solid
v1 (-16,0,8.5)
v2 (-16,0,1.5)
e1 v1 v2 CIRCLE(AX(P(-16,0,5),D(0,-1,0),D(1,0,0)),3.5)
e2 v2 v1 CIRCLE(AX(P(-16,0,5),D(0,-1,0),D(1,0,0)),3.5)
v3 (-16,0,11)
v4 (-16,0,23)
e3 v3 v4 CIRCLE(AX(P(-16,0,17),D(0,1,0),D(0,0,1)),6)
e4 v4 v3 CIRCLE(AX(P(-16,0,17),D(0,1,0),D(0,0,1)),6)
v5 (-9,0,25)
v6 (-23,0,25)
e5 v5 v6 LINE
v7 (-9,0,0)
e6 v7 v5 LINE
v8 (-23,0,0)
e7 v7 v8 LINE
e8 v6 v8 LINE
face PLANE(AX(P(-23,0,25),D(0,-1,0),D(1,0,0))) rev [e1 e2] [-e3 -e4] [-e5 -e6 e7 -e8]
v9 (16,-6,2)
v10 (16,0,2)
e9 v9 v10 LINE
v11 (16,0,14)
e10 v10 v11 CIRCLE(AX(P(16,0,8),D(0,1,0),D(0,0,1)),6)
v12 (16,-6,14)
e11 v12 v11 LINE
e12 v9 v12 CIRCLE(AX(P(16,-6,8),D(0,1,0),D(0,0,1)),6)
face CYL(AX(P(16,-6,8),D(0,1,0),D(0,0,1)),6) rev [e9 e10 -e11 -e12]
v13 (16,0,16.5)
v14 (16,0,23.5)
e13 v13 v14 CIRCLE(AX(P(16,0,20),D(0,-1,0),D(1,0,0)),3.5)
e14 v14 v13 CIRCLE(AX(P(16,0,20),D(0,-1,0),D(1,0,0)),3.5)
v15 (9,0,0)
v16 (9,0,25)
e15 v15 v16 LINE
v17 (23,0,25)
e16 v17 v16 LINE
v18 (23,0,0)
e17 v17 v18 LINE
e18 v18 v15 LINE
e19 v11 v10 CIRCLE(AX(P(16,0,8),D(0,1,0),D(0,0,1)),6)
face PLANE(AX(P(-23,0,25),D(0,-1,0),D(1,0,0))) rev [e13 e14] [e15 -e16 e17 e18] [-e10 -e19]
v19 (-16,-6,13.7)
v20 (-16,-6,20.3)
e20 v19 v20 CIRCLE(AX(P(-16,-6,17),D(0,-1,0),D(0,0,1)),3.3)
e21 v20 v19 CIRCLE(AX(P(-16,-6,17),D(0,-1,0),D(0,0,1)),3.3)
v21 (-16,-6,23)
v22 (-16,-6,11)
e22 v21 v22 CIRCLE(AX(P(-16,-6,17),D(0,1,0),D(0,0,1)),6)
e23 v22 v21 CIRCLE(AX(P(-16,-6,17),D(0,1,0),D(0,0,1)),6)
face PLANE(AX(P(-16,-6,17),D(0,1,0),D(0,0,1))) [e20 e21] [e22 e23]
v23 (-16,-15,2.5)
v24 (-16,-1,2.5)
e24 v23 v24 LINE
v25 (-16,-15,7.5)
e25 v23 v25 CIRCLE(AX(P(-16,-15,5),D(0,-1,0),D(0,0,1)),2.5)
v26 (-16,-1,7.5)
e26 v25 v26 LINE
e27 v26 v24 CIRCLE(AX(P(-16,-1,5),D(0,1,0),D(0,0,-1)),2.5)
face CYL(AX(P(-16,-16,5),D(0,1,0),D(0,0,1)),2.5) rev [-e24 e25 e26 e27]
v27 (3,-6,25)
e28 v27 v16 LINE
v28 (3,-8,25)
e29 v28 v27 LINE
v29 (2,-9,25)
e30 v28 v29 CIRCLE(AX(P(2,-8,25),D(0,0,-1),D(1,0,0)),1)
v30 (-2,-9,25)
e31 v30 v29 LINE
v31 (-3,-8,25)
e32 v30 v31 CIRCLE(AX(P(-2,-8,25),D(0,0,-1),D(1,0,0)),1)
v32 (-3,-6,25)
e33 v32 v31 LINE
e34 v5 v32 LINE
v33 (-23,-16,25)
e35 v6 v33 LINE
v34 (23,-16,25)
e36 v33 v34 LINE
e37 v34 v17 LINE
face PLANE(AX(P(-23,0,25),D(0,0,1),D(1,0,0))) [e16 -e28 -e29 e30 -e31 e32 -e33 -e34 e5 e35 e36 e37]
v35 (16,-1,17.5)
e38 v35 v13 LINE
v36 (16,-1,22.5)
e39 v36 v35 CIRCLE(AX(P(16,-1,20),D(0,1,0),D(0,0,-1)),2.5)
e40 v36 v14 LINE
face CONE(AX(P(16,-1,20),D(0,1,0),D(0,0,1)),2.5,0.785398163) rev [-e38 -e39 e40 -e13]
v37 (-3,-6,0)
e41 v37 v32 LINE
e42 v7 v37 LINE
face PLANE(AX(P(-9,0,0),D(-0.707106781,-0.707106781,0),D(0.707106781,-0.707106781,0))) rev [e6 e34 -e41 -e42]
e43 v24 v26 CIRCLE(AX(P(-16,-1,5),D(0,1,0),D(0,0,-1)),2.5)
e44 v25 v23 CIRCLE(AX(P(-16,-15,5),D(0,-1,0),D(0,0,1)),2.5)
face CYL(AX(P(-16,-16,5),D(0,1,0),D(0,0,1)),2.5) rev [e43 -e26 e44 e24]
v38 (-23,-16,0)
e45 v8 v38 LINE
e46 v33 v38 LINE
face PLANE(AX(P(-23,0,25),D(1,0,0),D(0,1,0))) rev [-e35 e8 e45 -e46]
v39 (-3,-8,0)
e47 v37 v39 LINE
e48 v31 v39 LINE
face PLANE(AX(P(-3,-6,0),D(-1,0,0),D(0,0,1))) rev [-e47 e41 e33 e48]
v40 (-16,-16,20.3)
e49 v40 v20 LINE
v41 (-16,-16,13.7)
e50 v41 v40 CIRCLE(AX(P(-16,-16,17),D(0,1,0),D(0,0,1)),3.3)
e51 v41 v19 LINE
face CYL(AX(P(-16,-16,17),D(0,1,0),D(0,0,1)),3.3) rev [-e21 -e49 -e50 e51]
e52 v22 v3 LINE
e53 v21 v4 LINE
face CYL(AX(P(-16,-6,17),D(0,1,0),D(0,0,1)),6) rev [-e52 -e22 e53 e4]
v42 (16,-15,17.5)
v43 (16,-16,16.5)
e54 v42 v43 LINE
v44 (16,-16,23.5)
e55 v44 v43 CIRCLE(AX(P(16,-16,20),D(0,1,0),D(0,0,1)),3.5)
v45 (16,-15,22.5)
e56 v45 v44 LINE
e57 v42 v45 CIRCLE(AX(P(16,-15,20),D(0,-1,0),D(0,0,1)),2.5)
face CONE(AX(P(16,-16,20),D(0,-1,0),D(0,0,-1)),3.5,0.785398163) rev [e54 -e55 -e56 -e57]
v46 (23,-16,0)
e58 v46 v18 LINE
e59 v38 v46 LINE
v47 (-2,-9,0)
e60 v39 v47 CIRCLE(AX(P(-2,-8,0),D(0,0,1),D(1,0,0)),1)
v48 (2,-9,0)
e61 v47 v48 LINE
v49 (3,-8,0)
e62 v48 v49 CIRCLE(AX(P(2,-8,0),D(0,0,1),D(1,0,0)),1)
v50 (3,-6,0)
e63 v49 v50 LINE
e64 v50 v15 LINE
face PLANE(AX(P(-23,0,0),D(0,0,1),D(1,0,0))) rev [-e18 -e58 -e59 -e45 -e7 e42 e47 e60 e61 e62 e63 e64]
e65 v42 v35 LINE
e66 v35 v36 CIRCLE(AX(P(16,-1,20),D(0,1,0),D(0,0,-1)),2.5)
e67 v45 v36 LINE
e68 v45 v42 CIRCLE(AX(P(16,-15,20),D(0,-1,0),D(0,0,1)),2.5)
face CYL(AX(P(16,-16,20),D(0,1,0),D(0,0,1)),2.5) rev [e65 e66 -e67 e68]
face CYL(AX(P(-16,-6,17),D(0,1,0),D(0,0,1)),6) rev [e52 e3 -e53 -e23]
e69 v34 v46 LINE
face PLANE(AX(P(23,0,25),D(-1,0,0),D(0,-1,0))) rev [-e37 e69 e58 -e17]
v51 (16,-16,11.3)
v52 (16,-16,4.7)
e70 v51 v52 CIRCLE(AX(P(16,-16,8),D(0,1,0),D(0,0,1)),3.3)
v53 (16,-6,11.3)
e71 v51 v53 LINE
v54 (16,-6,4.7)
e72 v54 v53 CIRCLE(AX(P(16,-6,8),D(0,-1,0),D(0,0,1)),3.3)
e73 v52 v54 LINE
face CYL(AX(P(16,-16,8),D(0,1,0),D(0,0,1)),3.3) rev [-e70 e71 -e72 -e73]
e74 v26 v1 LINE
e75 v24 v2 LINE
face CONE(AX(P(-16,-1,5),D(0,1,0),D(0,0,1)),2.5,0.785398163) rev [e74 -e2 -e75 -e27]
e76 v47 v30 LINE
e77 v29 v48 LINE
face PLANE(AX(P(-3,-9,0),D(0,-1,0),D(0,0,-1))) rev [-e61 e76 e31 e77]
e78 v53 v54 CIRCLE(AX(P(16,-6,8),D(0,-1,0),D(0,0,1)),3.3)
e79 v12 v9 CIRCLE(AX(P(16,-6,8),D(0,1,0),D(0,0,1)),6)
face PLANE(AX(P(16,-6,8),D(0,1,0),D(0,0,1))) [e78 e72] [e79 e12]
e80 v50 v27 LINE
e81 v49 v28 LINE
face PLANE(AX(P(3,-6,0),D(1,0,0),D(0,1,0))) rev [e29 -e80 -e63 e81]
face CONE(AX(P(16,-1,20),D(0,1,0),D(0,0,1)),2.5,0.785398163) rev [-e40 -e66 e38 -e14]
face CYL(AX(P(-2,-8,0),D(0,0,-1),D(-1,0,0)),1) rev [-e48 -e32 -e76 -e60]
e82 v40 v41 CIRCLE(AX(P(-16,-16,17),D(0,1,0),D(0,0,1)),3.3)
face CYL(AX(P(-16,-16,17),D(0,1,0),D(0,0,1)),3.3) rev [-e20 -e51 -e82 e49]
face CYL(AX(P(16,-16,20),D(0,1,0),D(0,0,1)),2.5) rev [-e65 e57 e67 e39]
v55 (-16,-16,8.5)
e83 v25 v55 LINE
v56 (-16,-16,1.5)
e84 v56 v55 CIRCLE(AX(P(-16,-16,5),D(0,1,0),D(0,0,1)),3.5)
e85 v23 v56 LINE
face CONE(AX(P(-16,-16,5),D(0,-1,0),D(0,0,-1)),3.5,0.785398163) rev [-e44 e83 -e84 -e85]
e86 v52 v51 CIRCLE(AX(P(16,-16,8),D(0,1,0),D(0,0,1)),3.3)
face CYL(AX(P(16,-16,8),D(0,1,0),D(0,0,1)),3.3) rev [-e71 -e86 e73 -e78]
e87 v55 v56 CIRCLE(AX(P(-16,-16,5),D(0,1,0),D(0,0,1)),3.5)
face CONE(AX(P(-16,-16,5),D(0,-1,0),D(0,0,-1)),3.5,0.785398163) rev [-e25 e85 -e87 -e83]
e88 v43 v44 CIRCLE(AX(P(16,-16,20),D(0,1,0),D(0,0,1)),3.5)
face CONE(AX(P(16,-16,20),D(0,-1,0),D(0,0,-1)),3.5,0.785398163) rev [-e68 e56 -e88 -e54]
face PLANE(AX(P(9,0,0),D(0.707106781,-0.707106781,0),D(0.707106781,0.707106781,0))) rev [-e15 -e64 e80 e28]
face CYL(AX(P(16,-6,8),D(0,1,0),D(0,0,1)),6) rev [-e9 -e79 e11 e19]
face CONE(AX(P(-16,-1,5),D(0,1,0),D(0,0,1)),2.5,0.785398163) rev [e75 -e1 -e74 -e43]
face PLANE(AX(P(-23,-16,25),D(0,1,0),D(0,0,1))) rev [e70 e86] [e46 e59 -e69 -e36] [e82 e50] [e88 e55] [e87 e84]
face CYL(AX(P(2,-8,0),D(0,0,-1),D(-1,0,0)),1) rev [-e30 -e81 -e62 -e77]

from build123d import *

# Parameters (mm, degrees)
SKETCH1_W          = 46
SKETCH1_H          = 16
BOSS_EXTRUDE_DEPTH = 25
CUT_EXTRUDE1_DEPTH = 38.549966711
SKETCH4_R          = 3.3
SKETCH4_R_2        = 2.5
CUT_EXTRUDE4_DEPTH = 38.549966711
FILLET1_R          = 1
FILLET2_R          = 1
SKETCH5_R          = 6
CUT_EXTRUDE5_DEPTH = 6
CHAMFER1_SIZE      = 1
CHAMFER2_SIZE      = 1
CHAMFER3_SIZE      = 1
CHAMFER4_SIZE      = 1


with BuildPart() as part:
    # Sketch1 → Boss-Extrude (new body)
    with BuildSketch(Plane.XY):
        with Locations((0, -8)):
            Rectangle(SKETCH1_W, SKETCH1_H)
    extrude(amount=BOSS_EXTRUDE_DEPTH)

    # Sketch2 → Cut-Extrude1 (cut, through all)
    with BuildSketch(Plane.XY.offset(25)):
        Polygon((-3, -9), (3, -9), (3, -6), (9, 0), (-9, 0), (-3, -6), align=None)
    extrude(amount=-CUT_EXTRUDE1_DEPTH, mode=Mode.SUBTRACT)

    # Sketch4 → Cut-Extrude4 (cut, through all)
    with BuildSketch(Plane(origin=(0, 0, 0), x_dir=(-1, 0, 0), z_dir=(0, 1, 0))):
        with Locations(Location((16, 17, 0), (0, 0, 90))):
            Circle(SKETCH4_R)
        with Locations(Location((16, 5, 0), (0, 0, 90))):
            Circle(SKETCH4_R_2)
        with Locations(Location((-16, 20, 0), (0, 0, 90))):
            Circle(SKETCH4_R_2)
        with Locations(Location((-16, 8, 0), (0, 0, 90))):
            Circle(SKETCH4_R)
    extrude(amount=-CUT_EXTRUDE4_DEPTH, mode=Mode.SUBTRACT)

    # Fillet1
    fillet1_edges = [part.edges().sort_by_distance(p)[0] for p in [
        (-3, -9, 12.5),
    ]]
    fillet(fillet1_edges, radius=FILLET1_R)

    # Fillet2
    fillet2_edges = [part.edges().sort_by_distance(p)[0] for p in [
        (3, -9, 12.5),
    ]]
    fillet(fillet2_edges, radius=FILLET2_R)

    # Sketch5 → Cut-Extrude5 (cut)
    with BuildSketch(Plane(origin=(0, 0, 0), x_dir=(-1, 0, 0), z_dir=(0, 1, 0))):
        with Locations(Location((16, 17, 0), (0, 0, 90))):
            Circle(SKETCH5_R)
        with Locations(Location((-16, 8, 0), (0, 0, 90))):
            Circle(SKETCH5_R)
    extrude(amount=-CUT_EXTRUDE5_DEPTH, mode=Mode.SUBTRACT)

    # Chamfer1
    chamfer1_edges = [part.edges().sort_by_distance(p)[0] for p in [
        (16, 0, 17.5),
    ]]
    chamfer(chamfer1_edges, length=CHAMFER1_SIZE)

    # Chamfer2
    chamfer2_edges = [part.edges().sort_by_distance(p)[0] for p in [
        (-16, 0, 2.5),
    ]]
    chamfer(chamfer2_edges, length=CHAMFER2_SIZE)

    # Chamfer3
    chamfer3_edges = [part.edges().sort_by_distance(p)[0] for p in [
        (16, -16, 17.5),
    ]]
    chamfer(chamfer3_edges, length=CHAMFER3_SIZE)

    # Chamfer4
    chamfer4_edges = [part.edges().sort_by_distance(p)[0] for p in [
        (-16, -16, 2.5),
    ]]
    chamfer(chamfer4_edges, length=CHAMFER4_SIZE)


solid = part.part
